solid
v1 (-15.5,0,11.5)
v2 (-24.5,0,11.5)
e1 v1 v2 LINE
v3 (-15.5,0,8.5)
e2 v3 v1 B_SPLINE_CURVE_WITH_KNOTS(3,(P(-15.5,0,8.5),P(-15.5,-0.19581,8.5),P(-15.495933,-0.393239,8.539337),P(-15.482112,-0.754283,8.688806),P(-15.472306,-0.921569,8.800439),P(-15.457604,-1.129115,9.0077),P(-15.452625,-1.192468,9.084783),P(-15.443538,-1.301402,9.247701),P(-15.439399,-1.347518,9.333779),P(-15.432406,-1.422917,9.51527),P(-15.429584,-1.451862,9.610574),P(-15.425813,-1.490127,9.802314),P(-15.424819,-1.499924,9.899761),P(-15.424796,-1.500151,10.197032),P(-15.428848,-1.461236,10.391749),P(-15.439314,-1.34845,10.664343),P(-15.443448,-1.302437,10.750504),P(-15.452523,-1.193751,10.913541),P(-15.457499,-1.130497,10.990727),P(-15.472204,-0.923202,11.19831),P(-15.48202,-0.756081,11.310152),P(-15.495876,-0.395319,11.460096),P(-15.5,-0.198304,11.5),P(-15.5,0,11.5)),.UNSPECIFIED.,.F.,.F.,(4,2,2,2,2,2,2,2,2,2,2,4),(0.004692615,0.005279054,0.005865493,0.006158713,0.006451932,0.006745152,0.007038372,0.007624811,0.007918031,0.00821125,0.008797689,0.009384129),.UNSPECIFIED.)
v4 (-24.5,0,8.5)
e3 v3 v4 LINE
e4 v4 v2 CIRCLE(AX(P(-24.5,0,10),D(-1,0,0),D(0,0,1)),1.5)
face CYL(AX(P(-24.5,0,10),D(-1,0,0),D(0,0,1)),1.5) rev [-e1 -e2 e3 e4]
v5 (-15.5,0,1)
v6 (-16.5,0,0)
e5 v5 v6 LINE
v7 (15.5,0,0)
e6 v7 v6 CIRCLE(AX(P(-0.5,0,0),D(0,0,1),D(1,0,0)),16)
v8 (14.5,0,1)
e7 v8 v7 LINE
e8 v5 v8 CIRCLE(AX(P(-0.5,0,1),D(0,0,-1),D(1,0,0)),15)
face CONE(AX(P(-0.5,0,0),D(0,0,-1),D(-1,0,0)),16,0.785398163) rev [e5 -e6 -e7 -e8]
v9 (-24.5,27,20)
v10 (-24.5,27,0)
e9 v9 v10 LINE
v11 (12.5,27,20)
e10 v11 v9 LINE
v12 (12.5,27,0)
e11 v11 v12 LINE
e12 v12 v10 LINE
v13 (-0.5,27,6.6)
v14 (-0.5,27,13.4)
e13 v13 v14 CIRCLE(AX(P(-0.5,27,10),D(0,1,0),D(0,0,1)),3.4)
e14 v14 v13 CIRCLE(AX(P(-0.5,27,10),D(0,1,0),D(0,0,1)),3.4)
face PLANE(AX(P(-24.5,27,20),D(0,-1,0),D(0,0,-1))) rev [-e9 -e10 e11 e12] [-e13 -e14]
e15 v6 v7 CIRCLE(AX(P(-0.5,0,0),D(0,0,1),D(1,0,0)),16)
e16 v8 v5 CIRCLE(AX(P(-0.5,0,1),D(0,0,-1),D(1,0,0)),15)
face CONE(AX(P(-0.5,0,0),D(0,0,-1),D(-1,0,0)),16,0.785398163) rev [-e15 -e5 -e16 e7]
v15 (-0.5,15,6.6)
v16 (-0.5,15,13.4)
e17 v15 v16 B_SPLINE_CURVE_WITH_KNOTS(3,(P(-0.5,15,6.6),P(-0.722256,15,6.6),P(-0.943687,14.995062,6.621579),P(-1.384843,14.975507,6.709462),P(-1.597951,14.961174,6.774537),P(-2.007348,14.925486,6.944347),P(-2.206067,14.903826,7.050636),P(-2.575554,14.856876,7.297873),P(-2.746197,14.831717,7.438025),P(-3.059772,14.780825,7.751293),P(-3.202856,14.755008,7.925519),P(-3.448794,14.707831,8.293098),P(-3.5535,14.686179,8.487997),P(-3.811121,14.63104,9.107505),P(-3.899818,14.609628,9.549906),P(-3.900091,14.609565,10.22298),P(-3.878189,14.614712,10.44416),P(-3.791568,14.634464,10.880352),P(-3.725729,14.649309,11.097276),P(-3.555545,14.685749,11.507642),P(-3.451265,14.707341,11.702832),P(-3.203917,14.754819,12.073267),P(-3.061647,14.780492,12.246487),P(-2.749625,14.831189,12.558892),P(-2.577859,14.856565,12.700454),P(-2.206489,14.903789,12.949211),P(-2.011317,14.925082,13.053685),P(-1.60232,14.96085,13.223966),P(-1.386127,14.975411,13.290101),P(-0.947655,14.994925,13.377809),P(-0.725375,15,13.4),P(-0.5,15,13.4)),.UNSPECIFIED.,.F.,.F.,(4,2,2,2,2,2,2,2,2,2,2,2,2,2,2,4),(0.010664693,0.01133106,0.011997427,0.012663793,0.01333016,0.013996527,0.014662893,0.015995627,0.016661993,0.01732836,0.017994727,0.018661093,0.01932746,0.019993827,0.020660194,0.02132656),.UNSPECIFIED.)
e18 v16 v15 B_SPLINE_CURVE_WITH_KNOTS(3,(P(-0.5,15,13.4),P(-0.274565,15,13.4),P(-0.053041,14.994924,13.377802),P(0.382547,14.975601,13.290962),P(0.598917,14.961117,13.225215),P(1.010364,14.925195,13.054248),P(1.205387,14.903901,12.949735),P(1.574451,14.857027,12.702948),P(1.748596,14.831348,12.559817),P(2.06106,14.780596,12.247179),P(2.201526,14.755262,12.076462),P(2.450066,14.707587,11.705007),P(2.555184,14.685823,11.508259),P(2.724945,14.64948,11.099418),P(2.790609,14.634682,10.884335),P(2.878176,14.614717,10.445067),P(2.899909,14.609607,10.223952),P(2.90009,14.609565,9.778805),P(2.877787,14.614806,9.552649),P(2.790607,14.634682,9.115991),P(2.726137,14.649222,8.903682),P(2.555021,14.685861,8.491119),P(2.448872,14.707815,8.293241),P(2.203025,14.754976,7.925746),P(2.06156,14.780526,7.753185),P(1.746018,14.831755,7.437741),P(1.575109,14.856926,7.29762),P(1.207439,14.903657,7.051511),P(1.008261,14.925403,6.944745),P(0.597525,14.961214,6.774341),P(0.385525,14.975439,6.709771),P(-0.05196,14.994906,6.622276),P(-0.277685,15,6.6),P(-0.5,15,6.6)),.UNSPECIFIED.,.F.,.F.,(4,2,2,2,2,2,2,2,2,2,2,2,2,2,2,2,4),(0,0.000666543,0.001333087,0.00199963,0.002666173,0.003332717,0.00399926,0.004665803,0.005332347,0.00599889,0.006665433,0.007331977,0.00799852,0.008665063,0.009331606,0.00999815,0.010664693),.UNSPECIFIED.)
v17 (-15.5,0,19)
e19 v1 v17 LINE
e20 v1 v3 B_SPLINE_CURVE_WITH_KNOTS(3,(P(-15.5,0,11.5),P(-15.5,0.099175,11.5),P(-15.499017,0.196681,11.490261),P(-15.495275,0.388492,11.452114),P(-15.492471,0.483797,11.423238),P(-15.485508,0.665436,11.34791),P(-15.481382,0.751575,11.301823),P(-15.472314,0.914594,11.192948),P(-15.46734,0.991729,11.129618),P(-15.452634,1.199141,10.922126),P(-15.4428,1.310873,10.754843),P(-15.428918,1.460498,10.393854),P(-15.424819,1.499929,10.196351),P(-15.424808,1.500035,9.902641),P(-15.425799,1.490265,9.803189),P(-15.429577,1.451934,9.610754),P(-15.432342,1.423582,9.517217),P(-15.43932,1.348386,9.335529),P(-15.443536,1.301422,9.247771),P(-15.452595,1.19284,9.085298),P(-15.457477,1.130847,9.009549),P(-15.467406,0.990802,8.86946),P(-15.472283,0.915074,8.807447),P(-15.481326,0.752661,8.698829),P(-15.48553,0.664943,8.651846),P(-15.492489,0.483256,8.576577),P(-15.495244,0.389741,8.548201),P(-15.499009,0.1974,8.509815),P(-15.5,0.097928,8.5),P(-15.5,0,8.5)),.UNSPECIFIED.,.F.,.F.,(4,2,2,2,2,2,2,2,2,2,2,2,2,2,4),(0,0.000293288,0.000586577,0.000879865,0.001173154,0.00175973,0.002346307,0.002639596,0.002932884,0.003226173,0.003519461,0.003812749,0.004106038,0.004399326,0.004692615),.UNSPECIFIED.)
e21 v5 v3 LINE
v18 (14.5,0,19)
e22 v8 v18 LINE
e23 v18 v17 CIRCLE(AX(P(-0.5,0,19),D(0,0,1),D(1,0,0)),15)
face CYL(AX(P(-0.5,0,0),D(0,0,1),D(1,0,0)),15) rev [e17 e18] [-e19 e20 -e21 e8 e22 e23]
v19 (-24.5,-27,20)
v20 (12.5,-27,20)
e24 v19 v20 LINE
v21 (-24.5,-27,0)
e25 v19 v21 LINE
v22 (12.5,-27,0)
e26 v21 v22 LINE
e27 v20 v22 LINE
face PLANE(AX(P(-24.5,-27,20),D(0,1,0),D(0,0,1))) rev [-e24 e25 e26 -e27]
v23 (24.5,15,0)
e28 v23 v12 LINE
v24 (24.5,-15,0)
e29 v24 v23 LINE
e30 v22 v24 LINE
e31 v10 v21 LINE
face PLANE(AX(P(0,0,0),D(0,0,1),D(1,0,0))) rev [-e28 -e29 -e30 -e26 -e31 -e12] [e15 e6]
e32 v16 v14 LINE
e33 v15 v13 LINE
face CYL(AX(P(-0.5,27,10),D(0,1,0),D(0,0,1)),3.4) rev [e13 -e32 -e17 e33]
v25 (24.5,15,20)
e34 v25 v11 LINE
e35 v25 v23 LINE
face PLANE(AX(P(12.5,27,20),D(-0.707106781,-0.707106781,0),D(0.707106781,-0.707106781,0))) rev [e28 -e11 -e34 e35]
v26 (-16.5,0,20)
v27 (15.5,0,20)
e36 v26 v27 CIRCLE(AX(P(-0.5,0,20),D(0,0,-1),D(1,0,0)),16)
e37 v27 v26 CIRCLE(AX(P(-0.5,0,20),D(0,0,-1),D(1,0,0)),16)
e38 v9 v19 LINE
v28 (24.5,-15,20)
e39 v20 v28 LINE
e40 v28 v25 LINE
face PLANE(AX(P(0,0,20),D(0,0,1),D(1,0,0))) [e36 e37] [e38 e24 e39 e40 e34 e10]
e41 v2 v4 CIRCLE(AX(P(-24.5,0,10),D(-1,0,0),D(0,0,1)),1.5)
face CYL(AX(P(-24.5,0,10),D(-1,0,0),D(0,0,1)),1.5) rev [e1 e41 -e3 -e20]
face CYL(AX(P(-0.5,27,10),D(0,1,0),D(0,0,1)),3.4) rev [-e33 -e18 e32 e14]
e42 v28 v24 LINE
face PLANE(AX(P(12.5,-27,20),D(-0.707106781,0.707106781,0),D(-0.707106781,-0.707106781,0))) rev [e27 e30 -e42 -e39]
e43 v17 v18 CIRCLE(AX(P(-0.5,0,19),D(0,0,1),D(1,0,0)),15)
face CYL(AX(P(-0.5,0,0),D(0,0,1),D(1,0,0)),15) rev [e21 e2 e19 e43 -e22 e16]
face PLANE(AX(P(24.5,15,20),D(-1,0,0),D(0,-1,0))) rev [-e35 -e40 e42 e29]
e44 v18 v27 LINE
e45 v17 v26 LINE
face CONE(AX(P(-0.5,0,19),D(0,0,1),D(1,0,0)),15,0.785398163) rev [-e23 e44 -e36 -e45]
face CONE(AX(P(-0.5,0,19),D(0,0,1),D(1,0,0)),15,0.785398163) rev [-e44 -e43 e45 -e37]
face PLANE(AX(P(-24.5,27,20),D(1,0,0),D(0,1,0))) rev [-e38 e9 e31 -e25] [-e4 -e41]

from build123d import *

# Parameters (mm, degrees)
BOSS_EXTRUDE1_DEPTH        = 20
SKETCH2_R                  = 15
CUT_EXTRUDE1_DEPTH         = 20
M8_TAPPED_HOLE1_D          = 6.8
M8_TAPPED_HOLE1_DEPTH      = 15
M8_TAPPED_HOLE1_TIP        = 2.042926105
CHAMFER2_SIZE              = 1
SIZE_MM_DOWEL_HOLE_1_D     = 3
SIZE_MM_DOWEL_HOLE_1_DEPTH = 19.75
SIZE_MM_DOWEL_HOLE_1_TIP   = 0.901290929


with BuildPart() as part:
    # Sketch1 → Boss-Extrude1 (new body)
    with BuildSketch(Plane.XY):
        Polygon((12.5, 27), (24.5, 15), (24.5, -15), (12.5, -27), (-24.5, -27), (-24.5, 27), align=None)
    extrude(amount=BOSS_EXTRUDE1_DEPTH)

    # Sketch2 → Cut-Extrude1 (cut)
    with BuildSketch(Plane.XY.offset(20)):
        with Locations((-0.5, 0)):
            Circle(SKETCH2_R)
    extrude(amount=-CUT_EXTRUDE1_DEPTH, mode=Mode.SUBTRACT)

    # M8 Tapped Hole1
    with Locations(Plane(origin=(-0.5, 27, 10), x_dir=(0, 0, 1), z_dir=(0, 1, 0))):
        with Locations((0, 0)):
            Hole(M8_TAPPED_HOLE1_D / 2, depth=M8_TAPPED_HOLE1_DEPTH)
            with Locations((0, 0, -(M8_TAPPED_HOLE1_DEPTH + M8_TAPPED_HOLE1_TIP / 2))):  # 118° drill point
                Cone(0, M8_TAPPED_HOLE1_D / 2, M8_TAPPED_HOLE1_TIP, mode=Mode.SUBTRACT)

    # Chamfer2
    chamfer2_edges = [part.edges().sort_by_distance(p)[0] for p in [
        (-15.5, 0, 0),
        (-15.5, 0, 20),
    ]]
    chamfer(chamfer2_edges, length=CHAMFER2_SIZE)

    # Size mm dowel hole 1
    with Locations(Plane(origin=(-24.5, 0, 10), x_dir=(0, -1, 0), z_dir=(-1, 0, 0))):
        with Locations((0, 0)):
            Hole(SIZE_MM_DOWEL_HOLE_1_D / 2, depth=SIZE_MM_DOWEL_HOLE_1_DEPTH)
            with Locations((0, 0, -(SIZE_MM_DOWEL_HOLE_1_DEPTH + SIZE_MM_DOWEL_HOLE_1_TIP / 2))):  # 118° drill point
                Cone(0, SIZE_MM_DOWEL_HOLE_1_D / 2, SIZE_MM_DOWEL_HOLE_1_TIP, mode=Mode.SUBTRACT)


solid = part.part
